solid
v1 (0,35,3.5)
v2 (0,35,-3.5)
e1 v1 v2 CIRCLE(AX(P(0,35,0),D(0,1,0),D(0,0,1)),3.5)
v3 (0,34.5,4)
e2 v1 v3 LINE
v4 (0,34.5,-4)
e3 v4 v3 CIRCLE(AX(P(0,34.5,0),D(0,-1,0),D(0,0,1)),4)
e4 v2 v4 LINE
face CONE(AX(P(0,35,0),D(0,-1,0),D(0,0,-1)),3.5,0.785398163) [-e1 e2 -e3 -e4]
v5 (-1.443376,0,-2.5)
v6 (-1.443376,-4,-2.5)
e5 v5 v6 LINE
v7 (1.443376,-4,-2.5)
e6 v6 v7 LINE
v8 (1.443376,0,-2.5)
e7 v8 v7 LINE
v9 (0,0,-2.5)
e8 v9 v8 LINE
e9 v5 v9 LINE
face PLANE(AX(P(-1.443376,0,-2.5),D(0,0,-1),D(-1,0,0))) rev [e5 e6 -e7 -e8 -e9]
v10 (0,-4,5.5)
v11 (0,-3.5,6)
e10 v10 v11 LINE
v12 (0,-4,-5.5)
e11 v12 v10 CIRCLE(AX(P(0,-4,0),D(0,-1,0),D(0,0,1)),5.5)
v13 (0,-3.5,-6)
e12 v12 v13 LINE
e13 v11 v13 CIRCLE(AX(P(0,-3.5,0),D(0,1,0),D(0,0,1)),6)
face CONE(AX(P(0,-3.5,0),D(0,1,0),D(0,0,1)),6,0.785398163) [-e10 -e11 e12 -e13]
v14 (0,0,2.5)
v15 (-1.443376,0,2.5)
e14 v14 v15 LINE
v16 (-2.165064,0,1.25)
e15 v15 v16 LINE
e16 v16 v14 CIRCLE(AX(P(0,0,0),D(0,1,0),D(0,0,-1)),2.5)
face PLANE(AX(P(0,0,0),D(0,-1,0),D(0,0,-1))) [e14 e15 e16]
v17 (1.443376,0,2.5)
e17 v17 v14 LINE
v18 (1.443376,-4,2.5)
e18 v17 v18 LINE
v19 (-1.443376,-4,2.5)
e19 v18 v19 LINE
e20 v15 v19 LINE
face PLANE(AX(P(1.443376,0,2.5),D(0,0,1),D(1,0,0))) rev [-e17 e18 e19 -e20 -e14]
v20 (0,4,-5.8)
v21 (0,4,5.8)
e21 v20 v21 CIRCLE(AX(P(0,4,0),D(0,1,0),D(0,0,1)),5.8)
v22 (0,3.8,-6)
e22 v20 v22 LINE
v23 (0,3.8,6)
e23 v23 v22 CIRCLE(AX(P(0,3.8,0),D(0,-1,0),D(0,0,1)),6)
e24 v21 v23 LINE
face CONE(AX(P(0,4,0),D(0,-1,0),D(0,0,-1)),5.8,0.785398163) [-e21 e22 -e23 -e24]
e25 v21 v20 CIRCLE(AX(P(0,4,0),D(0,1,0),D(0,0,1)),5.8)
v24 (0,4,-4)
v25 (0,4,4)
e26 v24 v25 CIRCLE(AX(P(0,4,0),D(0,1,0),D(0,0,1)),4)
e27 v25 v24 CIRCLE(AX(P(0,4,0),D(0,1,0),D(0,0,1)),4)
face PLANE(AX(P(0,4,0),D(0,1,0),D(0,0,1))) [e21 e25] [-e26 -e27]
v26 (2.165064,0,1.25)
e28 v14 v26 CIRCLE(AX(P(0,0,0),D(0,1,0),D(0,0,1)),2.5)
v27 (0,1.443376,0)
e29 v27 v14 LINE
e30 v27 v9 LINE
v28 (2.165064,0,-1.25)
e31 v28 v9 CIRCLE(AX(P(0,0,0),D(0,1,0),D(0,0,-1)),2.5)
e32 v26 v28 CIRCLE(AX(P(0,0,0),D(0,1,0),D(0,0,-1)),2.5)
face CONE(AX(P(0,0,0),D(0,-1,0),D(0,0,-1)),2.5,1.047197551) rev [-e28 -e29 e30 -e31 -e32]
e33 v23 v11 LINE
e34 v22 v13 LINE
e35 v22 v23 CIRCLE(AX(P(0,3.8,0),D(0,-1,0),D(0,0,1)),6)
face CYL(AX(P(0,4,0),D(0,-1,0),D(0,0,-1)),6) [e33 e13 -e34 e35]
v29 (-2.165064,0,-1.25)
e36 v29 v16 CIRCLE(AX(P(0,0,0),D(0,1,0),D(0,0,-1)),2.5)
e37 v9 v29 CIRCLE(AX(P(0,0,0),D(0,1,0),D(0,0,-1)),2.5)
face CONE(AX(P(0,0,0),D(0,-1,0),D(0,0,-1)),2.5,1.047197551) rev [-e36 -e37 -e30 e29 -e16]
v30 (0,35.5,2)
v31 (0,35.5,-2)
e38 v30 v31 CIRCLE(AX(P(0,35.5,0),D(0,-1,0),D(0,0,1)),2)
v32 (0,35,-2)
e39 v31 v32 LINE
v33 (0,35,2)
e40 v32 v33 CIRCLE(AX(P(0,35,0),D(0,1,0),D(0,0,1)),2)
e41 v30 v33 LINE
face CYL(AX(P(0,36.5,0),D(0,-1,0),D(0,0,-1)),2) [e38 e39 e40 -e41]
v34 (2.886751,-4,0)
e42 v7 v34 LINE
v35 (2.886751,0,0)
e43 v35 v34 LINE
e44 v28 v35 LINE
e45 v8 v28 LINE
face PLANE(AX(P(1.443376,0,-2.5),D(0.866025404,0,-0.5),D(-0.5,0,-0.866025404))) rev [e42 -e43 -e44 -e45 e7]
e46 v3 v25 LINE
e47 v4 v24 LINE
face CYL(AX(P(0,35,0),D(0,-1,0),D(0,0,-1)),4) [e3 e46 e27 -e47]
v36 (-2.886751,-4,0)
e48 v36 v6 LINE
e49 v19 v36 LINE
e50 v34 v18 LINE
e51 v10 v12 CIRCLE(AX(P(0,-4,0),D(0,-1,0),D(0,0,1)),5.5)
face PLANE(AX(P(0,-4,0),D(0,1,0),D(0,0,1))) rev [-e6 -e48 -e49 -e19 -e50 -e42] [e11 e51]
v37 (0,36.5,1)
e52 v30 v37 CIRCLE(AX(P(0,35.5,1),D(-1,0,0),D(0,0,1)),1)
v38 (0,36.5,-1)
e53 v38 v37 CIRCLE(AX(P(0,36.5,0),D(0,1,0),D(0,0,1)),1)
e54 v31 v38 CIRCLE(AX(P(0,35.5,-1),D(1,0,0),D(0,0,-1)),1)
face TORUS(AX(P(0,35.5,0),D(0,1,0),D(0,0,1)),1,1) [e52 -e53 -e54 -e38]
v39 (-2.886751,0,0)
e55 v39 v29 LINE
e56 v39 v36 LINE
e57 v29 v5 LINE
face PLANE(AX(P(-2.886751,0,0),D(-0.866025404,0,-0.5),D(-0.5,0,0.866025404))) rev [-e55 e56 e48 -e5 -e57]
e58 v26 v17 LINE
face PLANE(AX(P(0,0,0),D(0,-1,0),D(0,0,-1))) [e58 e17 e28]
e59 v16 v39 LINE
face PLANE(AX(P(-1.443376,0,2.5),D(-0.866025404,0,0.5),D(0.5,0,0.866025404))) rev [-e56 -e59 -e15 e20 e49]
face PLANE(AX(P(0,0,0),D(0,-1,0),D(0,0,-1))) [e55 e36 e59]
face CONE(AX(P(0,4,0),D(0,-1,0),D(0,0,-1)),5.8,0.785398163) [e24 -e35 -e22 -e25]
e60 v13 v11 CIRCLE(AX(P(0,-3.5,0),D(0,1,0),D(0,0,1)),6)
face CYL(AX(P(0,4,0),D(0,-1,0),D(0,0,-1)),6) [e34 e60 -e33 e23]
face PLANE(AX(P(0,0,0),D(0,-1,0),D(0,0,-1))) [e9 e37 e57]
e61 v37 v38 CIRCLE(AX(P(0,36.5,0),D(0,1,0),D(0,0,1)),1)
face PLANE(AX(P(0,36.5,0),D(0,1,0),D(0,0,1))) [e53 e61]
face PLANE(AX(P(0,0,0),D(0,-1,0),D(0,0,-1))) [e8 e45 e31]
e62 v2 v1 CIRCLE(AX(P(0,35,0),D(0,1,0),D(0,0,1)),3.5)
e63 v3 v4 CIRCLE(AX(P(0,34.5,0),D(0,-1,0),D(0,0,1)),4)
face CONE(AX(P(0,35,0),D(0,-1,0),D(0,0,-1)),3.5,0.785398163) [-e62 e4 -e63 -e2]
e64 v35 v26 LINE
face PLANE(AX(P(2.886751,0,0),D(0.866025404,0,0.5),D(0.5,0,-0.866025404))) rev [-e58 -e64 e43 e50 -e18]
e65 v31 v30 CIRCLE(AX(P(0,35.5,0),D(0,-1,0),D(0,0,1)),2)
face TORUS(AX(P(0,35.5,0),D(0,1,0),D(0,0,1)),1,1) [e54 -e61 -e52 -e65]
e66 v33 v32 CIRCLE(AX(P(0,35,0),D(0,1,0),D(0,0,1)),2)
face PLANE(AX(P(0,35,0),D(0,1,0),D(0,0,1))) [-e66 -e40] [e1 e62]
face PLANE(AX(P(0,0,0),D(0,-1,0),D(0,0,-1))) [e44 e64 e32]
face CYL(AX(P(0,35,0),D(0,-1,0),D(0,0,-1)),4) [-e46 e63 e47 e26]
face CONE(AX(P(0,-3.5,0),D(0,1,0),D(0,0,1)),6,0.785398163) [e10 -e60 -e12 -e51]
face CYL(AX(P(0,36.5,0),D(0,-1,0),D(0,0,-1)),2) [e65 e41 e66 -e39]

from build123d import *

# Parameters (mm, degrees)
SKETCH1_R           = 6
BOSS_EXTRUDE1_DEPTH = 4
SKETCH2_R           = 4
BOSS_EXTRUDE2_DEPTH = 31
SKETCH3_R           = 2
BOSS_EXTRUDE3_DEPTH = 1.5
CUT_EXTRUDE1_DEPTH  = 4
CHAMFER1_SIZE       = 0.5
CHAMFER2_SIZE       = 0.2
FILLET1_R           = 1


with BuildPart() as part:
    # Sketch1 → Boss-Extrude1 (new, symmetric)
    with BuildSketch(Plane(origin=(0, 0, 0), x_dir=(1, 0, 0), z_dir=(0, 1, 0))):
        with Locations(Location((0, 0, 0), (0, 0, 270))):
            Circle(SKETCH1_R)
    extrude(amount=BOSS_EXTRUDE1_DEPTH, both=True)

    # Sketch2 → Boss-Extrude2 (add)
    with BuildSketch(Plane(origin=(0, 4, 0), x_dir=(1, 0, 0), z_dir=(0, 1, 0))):
        with Locations(Location((0, 0, 0), (0, 0, 270))):
            Circle(SKETCH2_R)
    extrude(amount=BOSS_EXTRUDE2_DEPTH)

    # Sketch3 → Boss-Extrude3 (add)
    with BuildSketch(Plane(origin=(0, 35, 0), x_dir=(1, 0, 0), z_dir=(0, 1, 0))):
        with Locations(Location((0, 0, 0), (0, 0, 270))):
            Circle(SKETCH3_R)
    extrude(amount=BOSS_EXTRUDE3_DEPTH)

    # Sketch4 → Cut-Extrude1 (cut)
    with BuildSketch(Plane.XZ.offset(4)):
        Polygon((2.886751346, 0), (1.443375673, 2.5), (-1.443375673, 2.5), (-2.886751346, 0), (-1.443375673, -2.5), (1.443375673, -2.5), align=None)
    extrude(amount=-CUT_EXTRUDE1_DEPTH, mode=Mode.SUBTRACT)

    # Chamfer1
    chamfer1_edges = [part.edges().sort_by_distance(p)[0] for p in [
        (0, -4, -6),
        (0, 35, -4),
    ]]
    chamfer(chamfer1_edges, length=CHAMFER1_SIZE)

    # Chamfer2
    chamfer2_edges = [part.edges().sort_by_distance(p)[0] for p in [
        (0, 4, -6),
    ]]
    chamfer(chamfer2_edges, length=CHAMFER2_SIZE)

    # Fillet1
    fillet1_edges = [part.edges().sort_by_distance(p)[0] for p in [
        (0, 36.5, -2),
    ]]
    fillet(fillet1_edges, radius=FILLET1_R)

    # Sketch5 → Cut-Revolve1 (revolve, cut)
    with BuildSketch(Plane(origin=(0, 0, 0), x_dir=(0, 0, -1), z_dir=(1, 0, 0))):
        Polygon((2.5, 0), (0, 1.443375673), (0, 0), align=None)
    revolve(axis=Axis((0, 0, 0), (0, -1, 0)), mode=Mode.SUBTRACT)


solid = part.part
